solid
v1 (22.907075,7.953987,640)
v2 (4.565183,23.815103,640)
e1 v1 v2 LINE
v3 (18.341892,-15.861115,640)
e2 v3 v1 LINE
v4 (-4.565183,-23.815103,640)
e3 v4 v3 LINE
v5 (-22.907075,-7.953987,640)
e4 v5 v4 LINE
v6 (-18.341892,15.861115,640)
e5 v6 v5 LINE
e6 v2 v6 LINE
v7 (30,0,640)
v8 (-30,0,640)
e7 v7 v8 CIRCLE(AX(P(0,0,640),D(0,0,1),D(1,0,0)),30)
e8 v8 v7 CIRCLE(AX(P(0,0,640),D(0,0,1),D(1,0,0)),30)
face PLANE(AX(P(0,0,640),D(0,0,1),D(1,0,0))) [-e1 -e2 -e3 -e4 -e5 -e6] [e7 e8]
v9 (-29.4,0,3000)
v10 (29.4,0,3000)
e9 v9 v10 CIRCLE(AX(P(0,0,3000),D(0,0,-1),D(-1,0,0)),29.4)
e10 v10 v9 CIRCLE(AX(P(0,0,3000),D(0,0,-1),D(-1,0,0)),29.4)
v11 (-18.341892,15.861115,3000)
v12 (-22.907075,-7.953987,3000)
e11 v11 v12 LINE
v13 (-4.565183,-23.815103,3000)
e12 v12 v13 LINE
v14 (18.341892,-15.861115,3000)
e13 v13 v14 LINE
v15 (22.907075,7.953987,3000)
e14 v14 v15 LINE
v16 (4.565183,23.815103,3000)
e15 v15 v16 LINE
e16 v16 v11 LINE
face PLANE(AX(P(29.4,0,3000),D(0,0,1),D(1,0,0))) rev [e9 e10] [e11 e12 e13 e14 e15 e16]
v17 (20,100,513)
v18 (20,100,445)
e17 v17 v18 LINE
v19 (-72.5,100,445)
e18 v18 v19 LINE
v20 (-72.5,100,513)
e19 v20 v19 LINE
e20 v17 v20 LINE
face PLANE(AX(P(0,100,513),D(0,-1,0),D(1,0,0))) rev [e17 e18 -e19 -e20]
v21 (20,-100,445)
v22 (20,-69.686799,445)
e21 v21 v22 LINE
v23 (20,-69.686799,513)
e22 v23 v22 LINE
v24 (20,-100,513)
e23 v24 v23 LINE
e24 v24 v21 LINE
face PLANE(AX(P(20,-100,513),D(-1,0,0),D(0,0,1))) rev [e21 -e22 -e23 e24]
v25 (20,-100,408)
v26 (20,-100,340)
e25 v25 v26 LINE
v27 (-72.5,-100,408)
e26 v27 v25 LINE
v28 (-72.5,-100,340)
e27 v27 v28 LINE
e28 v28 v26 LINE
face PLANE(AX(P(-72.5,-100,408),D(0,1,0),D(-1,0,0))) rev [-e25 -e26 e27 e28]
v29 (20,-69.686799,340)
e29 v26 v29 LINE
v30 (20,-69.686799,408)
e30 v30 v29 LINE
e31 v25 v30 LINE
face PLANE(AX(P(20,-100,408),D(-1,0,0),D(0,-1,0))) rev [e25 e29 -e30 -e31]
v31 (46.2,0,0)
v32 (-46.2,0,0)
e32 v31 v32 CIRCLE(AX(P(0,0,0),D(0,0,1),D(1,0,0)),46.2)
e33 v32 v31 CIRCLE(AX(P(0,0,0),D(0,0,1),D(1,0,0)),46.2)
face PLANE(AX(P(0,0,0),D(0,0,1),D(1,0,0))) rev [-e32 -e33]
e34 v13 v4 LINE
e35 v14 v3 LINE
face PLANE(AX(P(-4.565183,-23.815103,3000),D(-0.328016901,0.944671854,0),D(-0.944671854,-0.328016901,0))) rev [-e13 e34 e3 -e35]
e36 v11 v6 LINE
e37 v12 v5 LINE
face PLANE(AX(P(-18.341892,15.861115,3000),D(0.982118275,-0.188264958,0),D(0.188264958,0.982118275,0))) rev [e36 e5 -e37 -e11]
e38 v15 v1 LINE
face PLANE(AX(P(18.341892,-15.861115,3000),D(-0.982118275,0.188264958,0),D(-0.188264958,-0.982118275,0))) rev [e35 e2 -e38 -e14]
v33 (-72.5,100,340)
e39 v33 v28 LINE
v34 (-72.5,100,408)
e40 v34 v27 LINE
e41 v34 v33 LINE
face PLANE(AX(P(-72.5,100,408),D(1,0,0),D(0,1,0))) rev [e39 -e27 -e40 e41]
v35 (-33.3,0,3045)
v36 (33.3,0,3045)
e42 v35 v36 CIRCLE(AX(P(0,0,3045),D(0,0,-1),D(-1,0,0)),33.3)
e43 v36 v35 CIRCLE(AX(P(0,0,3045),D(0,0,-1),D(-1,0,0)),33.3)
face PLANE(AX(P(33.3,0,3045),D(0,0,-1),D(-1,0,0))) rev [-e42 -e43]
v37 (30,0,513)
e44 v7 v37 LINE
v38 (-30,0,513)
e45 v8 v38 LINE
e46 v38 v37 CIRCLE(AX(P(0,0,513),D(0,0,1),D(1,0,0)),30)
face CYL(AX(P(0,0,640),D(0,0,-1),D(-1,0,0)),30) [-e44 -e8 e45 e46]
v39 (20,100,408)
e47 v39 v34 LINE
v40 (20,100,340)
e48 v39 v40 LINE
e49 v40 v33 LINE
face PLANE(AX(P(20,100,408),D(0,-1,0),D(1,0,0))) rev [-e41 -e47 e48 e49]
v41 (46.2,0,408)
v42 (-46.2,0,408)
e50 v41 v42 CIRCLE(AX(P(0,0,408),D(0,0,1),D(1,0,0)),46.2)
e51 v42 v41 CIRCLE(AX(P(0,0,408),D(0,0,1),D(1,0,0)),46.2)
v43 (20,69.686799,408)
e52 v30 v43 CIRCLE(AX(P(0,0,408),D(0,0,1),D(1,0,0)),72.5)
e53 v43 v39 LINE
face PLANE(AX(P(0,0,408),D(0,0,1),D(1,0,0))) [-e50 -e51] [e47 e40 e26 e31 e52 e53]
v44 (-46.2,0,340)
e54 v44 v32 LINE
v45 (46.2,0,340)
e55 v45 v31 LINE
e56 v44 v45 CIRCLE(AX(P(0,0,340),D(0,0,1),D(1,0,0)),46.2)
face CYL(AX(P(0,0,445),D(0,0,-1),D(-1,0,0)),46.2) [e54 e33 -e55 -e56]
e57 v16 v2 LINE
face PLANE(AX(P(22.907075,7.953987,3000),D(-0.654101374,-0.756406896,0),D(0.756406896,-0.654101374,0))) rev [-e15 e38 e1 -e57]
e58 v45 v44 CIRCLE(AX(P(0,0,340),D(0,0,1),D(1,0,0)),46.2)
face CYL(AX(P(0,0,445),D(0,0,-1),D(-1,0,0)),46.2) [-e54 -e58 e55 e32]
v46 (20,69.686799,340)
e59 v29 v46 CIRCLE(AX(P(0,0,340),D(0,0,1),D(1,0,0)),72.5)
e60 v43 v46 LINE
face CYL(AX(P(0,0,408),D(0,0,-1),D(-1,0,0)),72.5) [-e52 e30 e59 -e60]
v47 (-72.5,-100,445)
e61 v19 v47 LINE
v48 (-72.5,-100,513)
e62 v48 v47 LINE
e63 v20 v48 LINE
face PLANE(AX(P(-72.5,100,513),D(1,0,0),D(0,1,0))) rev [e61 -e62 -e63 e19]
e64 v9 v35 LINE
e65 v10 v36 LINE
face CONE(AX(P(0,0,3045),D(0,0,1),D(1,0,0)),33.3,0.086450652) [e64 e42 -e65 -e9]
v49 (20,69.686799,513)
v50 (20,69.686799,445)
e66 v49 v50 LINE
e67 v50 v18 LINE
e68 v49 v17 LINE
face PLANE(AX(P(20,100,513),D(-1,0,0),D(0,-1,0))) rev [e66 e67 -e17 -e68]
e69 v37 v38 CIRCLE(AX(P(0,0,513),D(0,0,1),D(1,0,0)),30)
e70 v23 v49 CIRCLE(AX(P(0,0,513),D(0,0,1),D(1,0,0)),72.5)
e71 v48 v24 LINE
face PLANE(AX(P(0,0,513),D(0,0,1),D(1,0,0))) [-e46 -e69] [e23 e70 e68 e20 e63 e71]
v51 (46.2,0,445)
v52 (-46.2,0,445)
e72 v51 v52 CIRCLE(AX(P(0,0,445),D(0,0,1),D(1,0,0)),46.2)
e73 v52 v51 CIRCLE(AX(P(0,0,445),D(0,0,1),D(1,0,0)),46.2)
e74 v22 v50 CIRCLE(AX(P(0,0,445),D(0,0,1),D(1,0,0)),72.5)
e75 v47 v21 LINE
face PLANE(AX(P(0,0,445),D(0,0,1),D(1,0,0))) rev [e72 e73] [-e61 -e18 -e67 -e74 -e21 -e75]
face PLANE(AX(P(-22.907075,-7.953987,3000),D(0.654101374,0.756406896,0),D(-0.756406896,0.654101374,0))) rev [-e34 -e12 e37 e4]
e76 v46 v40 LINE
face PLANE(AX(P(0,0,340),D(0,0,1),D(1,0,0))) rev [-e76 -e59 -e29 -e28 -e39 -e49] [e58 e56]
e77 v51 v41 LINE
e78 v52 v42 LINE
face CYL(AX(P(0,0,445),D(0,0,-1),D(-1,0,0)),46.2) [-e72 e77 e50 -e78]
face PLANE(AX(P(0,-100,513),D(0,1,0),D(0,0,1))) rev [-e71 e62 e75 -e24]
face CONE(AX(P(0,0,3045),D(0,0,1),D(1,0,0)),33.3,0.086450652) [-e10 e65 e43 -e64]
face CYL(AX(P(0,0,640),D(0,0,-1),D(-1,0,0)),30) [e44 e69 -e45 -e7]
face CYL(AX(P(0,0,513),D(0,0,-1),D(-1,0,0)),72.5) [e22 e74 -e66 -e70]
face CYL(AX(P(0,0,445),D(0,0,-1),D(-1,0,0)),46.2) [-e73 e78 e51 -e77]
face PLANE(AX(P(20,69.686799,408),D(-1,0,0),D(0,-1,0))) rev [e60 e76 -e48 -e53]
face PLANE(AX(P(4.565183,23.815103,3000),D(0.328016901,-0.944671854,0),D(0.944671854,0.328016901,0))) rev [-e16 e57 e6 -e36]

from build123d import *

# Parameters (mm, degrees)
SKETCH1_R           = 46.2
BOSS_EXTRUDE1_DEPTH = 445
SKETCH2_R           = 30
BOSS_EXTRUDE2_DEPTH = 195
BOSS_EXTRUDE3_DEPTH = 2360
BOSS_EXTRUDE4_DEPTH = 68
BOSS_EXTRUDE5_DEPTH = 68


with BuildPart() as part:
    # Sketch1 → Boss-Extrude1 (new body)
    with BuildSketch(Plane.XY):
        Circle(SKETCH1_R)
    extrude(amount=BOSS_EXTRUDE1_DEPTH)

    # Sketch2 → Boss-Extrude2 (add)
    with BuildSketch(Plane.XY.offset(445)):
        Circle(SKETCH2_R)
    extrude(amount=BOSS_EXTRUDE2_DEPTH)

    # Sketch3 → Boss-Extrude3 (add)
    with BuildSketch(Plane.XY.offset(640)):
        Polygon((18.341892461, -15.861115375), (22.907075078, 7.953987137), (4.565182616, 23.815102512), (-18.341892461, 15.861115375), (-22.907075078, -7.953987137), (-4.565182616, -23.815102512), align=None)
    extrude(amount=BOSS_EXTRUDE3_DEPTH)

    # Sketch4 → Revolve1 (revolve)
    with BuildSketch(Plane(origin=(0, 0, 0), x_dir=(1, 0, 0), z_dir=(0, 1, 0)), mode=Mode.PRIVATE) as revolve1_sk:
        Polygon((29.4, -3000), (0, -3000), (0, -3045), (33.3, -3045), align=None)
    revolve(revolve1_sk.sketch.rotate(Axis((0, 0, 0), (0, 0, 1)), 180), axis=Axis((0, 0, 0), (0, 0, 1)))

    # Sketch5 → Boss-Extrude4 (add)
    with BuildSketch(Plane.XY.offset(445)):
        with BuildLine():
            Line((0, 100), (-72.5, 100))
            Line((-72.5, 100), (-72.5, -100))
            Line((-72.5, -100), (0, -100))
            Line((0, -100), (20, -100))
            Line((20, -100), (20, -69.686799324))
            ThreePointArc((20, -69.686799324), (72.5, 0), (20, 69.686799324))
            Line((20, 69.686799324), (20, 100))
            Line((20, 100), (0, 100))
        make_face()
    extrude(amount=BOSS_EXTRUDE4_DEPTH)

    # Sketch6 → Boss-Extrude5 (add)
    with BuildSketch(Plane.XY.offset(340)):
        with BuildLine():
            Line((20, 100), (-72.5, 100))
            Line((-72.5, 100), (-72.5, -100))
            Line((-72.5, -100), (20, -100))
            Line((20, -100), (20, -69.686799324))
            ThreePointArc((20, -69.686799324), (72.5, 0), (20, 69.686799324))
            Line((20, 69.686799324), (20, 100))
        make_face()
    extrude(amount=BOSS_EXTRUDE5_DEPTH)


solid = part.part
